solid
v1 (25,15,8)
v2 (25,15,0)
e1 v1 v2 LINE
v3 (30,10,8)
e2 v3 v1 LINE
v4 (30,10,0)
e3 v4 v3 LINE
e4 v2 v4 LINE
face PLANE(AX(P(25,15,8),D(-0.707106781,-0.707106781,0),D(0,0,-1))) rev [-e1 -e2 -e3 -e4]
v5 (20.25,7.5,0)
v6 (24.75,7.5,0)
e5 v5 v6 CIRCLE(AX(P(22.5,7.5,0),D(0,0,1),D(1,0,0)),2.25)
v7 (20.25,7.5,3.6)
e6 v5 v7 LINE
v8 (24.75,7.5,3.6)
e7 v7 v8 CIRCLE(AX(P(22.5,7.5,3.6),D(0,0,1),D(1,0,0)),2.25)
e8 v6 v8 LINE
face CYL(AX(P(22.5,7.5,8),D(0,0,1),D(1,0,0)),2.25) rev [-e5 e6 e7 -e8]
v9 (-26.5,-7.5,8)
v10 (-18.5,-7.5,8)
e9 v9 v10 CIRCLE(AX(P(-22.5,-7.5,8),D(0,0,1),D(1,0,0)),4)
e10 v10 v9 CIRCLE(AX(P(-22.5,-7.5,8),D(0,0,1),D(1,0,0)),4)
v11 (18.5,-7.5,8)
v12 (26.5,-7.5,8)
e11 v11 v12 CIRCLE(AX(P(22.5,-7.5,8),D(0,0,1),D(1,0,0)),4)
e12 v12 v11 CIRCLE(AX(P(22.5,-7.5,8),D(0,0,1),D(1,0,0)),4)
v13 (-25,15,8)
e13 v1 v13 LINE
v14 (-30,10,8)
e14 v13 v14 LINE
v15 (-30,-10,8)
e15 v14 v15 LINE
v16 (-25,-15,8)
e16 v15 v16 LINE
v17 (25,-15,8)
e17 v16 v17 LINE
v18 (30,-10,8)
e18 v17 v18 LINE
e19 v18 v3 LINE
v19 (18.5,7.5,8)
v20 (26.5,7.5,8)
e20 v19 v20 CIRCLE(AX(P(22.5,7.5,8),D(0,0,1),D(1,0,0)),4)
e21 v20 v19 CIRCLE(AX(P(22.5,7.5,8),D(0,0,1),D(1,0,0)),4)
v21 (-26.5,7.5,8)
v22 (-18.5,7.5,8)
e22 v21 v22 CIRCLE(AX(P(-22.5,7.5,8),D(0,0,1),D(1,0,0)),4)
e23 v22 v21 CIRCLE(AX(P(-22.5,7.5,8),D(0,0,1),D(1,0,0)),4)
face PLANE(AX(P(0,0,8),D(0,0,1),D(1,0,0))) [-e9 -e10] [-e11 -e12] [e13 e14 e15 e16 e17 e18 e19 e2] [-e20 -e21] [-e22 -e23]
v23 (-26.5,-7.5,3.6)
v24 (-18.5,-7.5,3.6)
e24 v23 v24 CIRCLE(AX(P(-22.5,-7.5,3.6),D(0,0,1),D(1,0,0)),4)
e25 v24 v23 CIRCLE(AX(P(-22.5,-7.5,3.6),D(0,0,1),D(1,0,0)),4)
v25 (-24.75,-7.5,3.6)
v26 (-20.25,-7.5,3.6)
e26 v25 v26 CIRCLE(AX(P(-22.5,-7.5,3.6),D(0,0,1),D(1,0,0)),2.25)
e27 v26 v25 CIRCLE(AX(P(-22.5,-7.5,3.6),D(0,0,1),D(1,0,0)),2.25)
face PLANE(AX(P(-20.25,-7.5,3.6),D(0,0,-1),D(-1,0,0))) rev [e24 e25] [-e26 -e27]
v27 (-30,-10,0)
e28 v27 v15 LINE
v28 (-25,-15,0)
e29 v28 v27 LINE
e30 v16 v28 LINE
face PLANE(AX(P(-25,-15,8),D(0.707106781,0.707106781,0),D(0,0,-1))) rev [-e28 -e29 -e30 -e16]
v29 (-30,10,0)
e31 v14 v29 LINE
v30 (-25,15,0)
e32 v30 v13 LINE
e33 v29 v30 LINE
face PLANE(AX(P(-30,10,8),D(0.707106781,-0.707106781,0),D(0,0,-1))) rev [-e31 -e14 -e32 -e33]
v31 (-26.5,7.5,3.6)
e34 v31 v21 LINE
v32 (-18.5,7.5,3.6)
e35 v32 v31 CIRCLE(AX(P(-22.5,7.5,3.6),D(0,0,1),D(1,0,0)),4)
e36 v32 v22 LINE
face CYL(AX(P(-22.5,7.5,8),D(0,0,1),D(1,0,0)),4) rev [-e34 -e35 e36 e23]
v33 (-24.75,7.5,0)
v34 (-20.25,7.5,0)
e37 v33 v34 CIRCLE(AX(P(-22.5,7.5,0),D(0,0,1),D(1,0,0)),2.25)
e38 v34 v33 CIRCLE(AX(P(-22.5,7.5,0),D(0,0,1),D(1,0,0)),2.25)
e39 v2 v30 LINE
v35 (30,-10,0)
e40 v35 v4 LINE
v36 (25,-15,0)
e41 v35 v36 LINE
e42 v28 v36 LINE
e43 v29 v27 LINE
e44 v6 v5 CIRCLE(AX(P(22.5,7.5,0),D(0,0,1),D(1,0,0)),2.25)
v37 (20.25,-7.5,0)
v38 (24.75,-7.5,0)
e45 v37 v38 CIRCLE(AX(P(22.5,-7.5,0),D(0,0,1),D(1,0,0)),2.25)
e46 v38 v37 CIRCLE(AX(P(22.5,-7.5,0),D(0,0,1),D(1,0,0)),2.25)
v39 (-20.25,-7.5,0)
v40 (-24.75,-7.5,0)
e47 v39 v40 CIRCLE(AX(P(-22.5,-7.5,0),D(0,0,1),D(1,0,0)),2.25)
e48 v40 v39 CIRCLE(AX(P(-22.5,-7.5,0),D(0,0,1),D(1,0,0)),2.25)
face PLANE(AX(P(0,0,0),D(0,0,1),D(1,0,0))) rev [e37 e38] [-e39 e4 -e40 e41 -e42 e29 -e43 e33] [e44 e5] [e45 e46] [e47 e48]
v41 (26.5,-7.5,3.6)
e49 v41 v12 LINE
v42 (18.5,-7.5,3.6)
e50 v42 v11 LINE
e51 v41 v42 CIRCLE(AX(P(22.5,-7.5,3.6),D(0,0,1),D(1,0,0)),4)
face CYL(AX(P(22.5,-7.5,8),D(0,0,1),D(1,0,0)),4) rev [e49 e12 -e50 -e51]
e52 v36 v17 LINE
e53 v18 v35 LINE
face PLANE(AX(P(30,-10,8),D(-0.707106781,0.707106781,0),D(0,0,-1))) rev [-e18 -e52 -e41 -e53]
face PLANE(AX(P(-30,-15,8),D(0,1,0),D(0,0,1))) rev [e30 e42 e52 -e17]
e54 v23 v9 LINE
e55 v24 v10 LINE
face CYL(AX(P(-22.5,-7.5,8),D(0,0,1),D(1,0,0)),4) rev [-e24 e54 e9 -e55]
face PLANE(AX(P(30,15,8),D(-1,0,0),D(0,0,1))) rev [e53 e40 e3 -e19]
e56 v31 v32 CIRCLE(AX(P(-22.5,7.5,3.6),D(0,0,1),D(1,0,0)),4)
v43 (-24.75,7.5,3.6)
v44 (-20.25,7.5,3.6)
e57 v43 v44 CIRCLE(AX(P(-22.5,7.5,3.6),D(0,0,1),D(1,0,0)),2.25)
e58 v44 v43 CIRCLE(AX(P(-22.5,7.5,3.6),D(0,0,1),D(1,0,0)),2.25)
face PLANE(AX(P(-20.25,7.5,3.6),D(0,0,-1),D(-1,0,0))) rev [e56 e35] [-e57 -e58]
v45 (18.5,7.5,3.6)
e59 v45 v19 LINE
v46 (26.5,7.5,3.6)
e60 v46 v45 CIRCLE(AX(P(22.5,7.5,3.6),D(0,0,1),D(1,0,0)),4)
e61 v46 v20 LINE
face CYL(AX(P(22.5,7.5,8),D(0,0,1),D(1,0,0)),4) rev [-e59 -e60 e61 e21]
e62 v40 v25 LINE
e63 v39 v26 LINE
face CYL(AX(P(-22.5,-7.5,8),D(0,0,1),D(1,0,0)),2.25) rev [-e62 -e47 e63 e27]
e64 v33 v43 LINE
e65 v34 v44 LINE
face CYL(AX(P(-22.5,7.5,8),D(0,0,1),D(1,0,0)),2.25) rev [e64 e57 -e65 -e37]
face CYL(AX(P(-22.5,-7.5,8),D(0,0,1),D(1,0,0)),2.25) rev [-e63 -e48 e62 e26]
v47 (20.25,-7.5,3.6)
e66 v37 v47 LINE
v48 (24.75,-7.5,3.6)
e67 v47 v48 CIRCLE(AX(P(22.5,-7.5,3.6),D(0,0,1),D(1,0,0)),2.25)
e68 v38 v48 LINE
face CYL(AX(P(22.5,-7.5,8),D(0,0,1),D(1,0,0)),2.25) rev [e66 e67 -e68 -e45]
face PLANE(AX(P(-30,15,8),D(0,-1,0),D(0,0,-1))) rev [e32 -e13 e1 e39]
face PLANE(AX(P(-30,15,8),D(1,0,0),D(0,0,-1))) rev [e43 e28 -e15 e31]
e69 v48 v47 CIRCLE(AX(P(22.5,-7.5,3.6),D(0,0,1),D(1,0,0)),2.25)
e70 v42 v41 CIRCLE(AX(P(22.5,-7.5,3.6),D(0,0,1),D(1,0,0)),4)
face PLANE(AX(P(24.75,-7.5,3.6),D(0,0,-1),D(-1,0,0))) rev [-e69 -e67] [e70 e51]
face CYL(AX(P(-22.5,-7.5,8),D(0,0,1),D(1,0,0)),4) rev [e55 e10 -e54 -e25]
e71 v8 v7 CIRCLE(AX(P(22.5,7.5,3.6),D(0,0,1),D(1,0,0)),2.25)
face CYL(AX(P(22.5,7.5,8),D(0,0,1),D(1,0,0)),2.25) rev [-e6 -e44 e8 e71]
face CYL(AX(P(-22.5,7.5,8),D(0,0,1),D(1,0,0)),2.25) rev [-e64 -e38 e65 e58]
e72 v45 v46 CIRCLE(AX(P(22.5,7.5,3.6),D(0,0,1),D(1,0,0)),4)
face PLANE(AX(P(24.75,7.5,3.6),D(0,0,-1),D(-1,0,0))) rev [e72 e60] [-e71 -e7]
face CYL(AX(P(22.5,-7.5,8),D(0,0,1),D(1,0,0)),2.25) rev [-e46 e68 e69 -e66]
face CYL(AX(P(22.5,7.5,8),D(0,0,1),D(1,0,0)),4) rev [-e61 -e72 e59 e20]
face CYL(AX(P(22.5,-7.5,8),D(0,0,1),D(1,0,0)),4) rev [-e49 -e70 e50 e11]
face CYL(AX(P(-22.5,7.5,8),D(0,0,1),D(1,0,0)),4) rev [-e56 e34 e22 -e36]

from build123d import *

# Parameters (mm, degrees)
SKETCH1_W                                           = 60
SKETCH1_H                                           = 30
BOSS_EXTRUDE1_DEPTH                                 = 8
CBORE_FOR_M4_HEX_SOCKET_HEAD_CAP_SCREW1_D           = 4.5
CBORE_FOR_M4_HEX_SOCKET_HEAD_CAP_SCREW1_CBORE_D     = 8
CBORE_FOR_M4_HEX_SOCKET_HEAD_CAP_SCREW1_CBORE_DEPTH = 4.4
CHAMFER1_SIZE                                       = 5


with BuildPart() as part:
    # Sketch1 → Boss-Extrude1 (new body)
    with BuildSketch(Plane.XY):
        Rectangle(SKETCH1_W, SKETCH1_H)
    extrude(amount=BOSS_EXTRUDE1_DEPTH)

    # CBORE for M4 Hex Socket Head Cap Screw1 (through all)
    with Locations(Plane.XY.offset(8)):
        with Locations((22.5, 7.5), (-22.5, 7.5), (-22.5, -7.5), (22.5, -7.5)):
            CounterBoreHole(CBORE_FOR_M4_HEX_SOCKET_HEAD_CAP_SCREW1_D / 2, CBORE_FOR_M4_HEX_SOCKET_HEAD_CAP_SCREW1_CBORE_D / 2, CBORE_FOR_M4_HEX_SOCKET_HEAD_CAP_SCREW1_CBORE_DEPTH)

    # Chamfer1
    chamfer1_edges = [part.edges().sort_by_distance(p)[0] for p in [
        (30, -15, 4),
        (-30, -15, 4),
        (-30, 15, 4),
        (30, 15, 4),
    ]]
    chamfer(chamfer1_edges, length=CHAMFER1_SIZE)


solid = part.part
